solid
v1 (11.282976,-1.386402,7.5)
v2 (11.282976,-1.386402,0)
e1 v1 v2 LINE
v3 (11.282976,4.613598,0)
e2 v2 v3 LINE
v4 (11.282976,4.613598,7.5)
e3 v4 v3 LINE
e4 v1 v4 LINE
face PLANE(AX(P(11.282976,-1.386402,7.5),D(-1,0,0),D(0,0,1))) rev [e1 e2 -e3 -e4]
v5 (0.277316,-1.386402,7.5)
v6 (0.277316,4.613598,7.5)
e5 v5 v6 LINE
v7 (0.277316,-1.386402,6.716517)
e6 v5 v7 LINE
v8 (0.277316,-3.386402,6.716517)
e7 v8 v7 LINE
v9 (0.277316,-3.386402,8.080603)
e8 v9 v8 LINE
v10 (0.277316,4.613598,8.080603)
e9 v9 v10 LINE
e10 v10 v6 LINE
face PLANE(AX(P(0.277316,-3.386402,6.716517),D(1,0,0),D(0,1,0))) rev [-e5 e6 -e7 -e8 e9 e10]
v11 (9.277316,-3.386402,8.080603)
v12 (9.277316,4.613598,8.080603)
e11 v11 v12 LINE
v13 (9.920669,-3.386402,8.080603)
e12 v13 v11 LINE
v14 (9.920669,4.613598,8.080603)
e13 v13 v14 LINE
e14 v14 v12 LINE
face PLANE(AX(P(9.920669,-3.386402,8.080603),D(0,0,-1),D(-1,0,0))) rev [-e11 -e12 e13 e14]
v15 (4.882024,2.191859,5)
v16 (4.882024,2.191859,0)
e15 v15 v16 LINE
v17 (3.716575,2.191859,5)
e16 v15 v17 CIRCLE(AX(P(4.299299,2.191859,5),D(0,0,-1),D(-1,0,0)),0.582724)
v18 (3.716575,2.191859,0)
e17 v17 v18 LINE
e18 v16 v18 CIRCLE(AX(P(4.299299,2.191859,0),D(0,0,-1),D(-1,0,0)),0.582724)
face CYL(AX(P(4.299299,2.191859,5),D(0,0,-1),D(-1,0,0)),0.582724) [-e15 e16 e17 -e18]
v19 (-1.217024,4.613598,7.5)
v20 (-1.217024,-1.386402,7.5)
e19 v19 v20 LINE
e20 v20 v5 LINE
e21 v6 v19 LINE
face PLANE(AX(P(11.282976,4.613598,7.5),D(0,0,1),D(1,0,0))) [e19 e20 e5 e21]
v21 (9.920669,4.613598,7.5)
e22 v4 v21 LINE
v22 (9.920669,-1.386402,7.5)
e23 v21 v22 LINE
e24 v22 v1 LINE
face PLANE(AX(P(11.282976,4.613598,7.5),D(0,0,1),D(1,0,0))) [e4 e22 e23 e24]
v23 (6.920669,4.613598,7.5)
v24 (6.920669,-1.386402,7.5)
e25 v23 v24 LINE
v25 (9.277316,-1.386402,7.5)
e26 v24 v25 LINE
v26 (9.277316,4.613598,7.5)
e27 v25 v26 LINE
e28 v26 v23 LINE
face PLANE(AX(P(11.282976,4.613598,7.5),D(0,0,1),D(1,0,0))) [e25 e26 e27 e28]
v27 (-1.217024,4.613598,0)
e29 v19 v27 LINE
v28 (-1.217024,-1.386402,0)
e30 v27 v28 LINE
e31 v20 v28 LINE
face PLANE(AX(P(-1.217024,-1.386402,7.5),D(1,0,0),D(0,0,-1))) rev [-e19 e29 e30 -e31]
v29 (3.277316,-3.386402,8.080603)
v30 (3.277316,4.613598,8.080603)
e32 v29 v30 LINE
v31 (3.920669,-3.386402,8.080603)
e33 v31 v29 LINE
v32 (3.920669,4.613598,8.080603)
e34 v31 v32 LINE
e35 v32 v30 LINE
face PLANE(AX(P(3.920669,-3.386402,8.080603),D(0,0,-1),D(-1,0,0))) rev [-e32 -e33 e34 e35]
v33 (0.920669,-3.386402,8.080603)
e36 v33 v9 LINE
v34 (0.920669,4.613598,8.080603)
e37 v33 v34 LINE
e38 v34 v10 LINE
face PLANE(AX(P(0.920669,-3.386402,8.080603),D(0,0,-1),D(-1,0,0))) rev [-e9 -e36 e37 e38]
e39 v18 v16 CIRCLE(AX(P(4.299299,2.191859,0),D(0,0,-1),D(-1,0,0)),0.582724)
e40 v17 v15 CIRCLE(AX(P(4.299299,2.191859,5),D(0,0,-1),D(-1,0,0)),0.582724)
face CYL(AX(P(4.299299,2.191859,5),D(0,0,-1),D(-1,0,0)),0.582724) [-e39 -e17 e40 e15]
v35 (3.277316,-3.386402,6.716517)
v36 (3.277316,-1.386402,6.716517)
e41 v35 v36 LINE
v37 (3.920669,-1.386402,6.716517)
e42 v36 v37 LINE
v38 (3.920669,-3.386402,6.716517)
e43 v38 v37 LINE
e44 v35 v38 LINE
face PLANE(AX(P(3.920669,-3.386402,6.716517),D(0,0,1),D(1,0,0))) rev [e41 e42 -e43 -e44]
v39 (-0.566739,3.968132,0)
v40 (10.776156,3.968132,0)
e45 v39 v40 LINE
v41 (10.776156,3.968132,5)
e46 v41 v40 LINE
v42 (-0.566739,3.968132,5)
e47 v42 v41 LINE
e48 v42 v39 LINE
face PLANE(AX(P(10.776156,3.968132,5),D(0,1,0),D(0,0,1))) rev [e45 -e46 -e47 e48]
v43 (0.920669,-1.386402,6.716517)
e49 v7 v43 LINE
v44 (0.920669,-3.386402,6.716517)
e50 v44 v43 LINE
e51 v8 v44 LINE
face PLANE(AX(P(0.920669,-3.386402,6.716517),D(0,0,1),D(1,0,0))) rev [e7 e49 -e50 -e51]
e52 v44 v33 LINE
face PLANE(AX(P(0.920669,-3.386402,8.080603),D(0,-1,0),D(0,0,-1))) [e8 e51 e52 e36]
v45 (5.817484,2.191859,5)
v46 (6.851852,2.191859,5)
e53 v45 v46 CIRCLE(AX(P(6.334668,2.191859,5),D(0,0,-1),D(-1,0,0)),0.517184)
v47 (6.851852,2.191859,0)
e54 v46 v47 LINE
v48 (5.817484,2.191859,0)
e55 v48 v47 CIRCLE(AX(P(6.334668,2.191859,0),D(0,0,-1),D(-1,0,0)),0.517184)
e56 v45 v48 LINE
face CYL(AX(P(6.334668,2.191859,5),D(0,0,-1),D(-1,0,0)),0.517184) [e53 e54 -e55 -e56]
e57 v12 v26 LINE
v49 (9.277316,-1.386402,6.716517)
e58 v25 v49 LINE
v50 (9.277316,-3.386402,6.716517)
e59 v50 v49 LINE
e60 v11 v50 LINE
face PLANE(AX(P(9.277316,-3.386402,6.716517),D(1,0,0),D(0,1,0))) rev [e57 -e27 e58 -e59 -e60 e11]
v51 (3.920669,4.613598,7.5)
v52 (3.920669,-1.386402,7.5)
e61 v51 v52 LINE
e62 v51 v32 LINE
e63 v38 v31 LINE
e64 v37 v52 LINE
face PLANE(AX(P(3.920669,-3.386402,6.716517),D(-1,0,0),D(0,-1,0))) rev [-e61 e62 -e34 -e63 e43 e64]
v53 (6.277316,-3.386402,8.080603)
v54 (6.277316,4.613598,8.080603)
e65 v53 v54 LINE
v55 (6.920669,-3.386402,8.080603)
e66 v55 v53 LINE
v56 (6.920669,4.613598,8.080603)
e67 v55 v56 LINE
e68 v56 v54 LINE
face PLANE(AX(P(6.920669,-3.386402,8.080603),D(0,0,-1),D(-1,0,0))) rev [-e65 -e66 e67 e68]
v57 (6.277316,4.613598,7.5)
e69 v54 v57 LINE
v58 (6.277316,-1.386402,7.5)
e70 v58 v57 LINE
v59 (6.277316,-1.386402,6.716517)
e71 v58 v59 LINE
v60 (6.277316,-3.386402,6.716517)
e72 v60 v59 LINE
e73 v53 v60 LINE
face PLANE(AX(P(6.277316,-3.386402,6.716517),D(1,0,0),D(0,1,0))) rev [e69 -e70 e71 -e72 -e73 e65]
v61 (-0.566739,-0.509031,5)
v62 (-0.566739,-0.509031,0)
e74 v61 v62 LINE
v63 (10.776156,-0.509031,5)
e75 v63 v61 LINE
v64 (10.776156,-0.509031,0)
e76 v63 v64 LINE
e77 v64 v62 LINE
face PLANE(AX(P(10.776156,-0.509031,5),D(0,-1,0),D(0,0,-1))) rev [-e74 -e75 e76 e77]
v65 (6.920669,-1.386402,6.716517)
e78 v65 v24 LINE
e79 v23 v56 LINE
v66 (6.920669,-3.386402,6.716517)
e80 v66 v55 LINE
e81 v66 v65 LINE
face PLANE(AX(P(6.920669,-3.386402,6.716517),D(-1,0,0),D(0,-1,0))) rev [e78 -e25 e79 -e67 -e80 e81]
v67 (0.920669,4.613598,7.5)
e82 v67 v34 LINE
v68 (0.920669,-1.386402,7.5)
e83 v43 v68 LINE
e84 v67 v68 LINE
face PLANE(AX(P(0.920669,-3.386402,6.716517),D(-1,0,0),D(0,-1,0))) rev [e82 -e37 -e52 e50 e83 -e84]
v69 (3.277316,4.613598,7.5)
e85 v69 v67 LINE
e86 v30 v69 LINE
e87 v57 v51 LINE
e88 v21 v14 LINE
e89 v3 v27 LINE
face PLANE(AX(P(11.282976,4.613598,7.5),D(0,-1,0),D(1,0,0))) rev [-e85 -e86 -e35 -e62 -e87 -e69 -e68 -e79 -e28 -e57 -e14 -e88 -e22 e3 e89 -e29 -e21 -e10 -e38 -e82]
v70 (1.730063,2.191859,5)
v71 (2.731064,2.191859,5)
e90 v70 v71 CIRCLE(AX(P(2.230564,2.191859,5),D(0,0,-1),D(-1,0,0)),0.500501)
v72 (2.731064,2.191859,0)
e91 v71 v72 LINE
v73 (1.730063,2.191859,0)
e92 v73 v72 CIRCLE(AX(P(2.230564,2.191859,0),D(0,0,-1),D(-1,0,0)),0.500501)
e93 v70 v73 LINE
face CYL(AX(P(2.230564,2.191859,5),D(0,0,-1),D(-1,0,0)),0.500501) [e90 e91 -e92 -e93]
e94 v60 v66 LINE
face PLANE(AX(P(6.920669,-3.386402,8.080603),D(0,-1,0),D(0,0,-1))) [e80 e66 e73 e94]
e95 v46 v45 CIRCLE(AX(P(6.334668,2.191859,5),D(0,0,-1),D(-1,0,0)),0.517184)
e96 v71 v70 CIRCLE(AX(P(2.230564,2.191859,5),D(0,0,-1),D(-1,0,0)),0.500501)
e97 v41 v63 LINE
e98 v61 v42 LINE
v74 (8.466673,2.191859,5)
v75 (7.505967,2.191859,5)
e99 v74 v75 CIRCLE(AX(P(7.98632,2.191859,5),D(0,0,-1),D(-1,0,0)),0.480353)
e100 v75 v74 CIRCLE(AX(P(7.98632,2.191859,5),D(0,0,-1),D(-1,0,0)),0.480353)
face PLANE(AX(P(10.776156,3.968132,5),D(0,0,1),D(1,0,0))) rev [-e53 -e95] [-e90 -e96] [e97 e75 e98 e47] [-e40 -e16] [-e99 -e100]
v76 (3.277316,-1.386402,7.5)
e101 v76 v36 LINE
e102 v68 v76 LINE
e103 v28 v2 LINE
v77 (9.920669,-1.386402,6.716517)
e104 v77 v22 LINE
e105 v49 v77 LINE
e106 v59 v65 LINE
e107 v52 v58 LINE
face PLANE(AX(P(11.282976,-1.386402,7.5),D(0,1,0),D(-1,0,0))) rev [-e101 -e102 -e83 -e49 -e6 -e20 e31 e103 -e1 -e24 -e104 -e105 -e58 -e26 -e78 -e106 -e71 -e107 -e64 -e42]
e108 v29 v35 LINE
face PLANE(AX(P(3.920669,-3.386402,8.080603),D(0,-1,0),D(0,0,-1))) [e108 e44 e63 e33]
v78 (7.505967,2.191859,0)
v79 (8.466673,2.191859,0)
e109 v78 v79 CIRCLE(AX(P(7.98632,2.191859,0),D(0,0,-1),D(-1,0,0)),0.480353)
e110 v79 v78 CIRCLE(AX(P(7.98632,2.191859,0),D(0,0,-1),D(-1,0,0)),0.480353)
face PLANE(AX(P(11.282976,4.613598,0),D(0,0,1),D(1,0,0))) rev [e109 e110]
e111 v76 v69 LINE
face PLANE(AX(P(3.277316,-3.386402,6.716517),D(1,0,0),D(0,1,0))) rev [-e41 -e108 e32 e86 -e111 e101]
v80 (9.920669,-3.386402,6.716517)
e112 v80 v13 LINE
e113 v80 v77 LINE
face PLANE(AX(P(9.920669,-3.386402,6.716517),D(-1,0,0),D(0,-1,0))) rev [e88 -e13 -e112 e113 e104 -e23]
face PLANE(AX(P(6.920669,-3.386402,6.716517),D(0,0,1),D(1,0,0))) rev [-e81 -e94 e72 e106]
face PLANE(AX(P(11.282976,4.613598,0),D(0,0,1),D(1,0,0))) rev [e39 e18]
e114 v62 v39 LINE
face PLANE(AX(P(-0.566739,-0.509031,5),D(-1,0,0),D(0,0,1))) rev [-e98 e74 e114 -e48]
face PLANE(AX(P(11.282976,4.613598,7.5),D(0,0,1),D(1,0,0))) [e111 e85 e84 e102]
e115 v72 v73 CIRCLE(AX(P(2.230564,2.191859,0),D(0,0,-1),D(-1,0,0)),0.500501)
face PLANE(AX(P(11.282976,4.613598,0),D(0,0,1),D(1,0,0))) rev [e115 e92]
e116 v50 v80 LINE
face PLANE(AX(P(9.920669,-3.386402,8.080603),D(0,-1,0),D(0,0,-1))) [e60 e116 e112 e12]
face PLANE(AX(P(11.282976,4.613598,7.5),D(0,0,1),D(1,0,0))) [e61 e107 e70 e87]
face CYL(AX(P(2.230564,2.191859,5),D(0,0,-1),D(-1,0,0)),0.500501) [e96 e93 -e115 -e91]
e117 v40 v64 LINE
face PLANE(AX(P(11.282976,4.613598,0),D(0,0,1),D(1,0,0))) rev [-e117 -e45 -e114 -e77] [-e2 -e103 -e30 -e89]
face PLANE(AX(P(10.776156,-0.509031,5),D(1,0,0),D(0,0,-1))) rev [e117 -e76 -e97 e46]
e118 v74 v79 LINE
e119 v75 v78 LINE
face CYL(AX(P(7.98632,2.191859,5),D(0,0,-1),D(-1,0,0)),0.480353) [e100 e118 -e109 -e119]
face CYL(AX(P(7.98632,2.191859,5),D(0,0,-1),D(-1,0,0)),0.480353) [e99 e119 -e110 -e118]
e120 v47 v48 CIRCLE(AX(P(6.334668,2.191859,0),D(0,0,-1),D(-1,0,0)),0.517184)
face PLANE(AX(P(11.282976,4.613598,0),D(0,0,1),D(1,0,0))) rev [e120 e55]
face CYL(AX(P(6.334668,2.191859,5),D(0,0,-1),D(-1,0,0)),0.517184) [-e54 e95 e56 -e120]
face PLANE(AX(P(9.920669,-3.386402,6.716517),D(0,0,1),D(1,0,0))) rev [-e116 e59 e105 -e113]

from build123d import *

# Parameters (mm, degrees)
SKETCH_1_W          = 12.5
SKETCH_1_H          = 6
EXTRUDE_1_DEPTH     = 7.5
SKETCH_2_W          = 11.342894438
SKETCH_2_H          = 4.477163802
SKETCH_2_R          = 0.480353021
SKETCH_2_R_2        = 0.517183851
SKETCH_2_R_3        = 0.582724364
SKETCH_2_R_4        = 0.500500501
CUT_EXTRUDE_1_DEPTH = 5
SKETCH_3_W          = 0.643352529
SKETCH_3_H          = 1.364086891
EXTRUDE_2_DEPTH     = 8


with BuildPart() as part:
    # 草图1 → 拉伸1 (new body)
    with BuildSketch(Plane.XY):
        with Locations((5.032975889, 1.613598403)):
            Rectangle(SKETCH_1_W, SKETCH_1_H)
    extrude(amount=EXTRUDE_1_DEPTH)

    # 草图2 → 切除-拉伸1 (cut)
    with BuildSketch(Plane(origin=(0, 0, 0), x_dir=(-1, 0, 0), z_dir=(0, 0, -1))):
        with Locations((-5.104708636, 1.729550555)):
            Rectangle(SKETCH_2_W, SKETCH_2_H)
        with Locations((-7.986319653, 2.191858525)):
            Circle(SKETCH_2_R, mode=Mode.SUBTRACT)
        with Locations((-6.334668001, 2.191858525)):
            Circle(SKETCH_2_R_2, mode=Mode.SUBTRACT)
        with Locations((-4.299299299, 2.191858525)):
            Circle(SKETCH_2_R_3, mode=Mode.SUBTRACT)
        with Locations((-2.230563897, 2.191858525)):
            Circle(SKETCH_2_R_4, mode=Mode.SUBTRACT)
    extrude(amount=-CUT_EXTRUDE_1_DEPTH, mode=Mode.SUBTRACT)

    # 草图3 → 拉伸2 (add)
    with BuildSketch(Plane(origin=(0, 4.613598403, 4.886401597), x_dir=(1, 0, 0), z_dir=(0, -1, 0))):
        with Locations((6.598992375, 2.512158379)):
            Rectangle(SKETCH_3_W, SKETCH_3_H)
        with Locations((9.598992375, 2.512158379)):
            Rectangle(SKETCH_3_W, SKETCH_3_H)
        with Locations((3.598992375, 2.512158379)):
            Rectangle(SKETCH_3_W, SKETCH_3_H)
        with Locations((0.598992376, 2.512158379)):
            Rectangle(SKETCH_3_W, SKETCH_3_H)
    extrude(amount=EXTRUDE_2_DEPTH)


solid = part.part
